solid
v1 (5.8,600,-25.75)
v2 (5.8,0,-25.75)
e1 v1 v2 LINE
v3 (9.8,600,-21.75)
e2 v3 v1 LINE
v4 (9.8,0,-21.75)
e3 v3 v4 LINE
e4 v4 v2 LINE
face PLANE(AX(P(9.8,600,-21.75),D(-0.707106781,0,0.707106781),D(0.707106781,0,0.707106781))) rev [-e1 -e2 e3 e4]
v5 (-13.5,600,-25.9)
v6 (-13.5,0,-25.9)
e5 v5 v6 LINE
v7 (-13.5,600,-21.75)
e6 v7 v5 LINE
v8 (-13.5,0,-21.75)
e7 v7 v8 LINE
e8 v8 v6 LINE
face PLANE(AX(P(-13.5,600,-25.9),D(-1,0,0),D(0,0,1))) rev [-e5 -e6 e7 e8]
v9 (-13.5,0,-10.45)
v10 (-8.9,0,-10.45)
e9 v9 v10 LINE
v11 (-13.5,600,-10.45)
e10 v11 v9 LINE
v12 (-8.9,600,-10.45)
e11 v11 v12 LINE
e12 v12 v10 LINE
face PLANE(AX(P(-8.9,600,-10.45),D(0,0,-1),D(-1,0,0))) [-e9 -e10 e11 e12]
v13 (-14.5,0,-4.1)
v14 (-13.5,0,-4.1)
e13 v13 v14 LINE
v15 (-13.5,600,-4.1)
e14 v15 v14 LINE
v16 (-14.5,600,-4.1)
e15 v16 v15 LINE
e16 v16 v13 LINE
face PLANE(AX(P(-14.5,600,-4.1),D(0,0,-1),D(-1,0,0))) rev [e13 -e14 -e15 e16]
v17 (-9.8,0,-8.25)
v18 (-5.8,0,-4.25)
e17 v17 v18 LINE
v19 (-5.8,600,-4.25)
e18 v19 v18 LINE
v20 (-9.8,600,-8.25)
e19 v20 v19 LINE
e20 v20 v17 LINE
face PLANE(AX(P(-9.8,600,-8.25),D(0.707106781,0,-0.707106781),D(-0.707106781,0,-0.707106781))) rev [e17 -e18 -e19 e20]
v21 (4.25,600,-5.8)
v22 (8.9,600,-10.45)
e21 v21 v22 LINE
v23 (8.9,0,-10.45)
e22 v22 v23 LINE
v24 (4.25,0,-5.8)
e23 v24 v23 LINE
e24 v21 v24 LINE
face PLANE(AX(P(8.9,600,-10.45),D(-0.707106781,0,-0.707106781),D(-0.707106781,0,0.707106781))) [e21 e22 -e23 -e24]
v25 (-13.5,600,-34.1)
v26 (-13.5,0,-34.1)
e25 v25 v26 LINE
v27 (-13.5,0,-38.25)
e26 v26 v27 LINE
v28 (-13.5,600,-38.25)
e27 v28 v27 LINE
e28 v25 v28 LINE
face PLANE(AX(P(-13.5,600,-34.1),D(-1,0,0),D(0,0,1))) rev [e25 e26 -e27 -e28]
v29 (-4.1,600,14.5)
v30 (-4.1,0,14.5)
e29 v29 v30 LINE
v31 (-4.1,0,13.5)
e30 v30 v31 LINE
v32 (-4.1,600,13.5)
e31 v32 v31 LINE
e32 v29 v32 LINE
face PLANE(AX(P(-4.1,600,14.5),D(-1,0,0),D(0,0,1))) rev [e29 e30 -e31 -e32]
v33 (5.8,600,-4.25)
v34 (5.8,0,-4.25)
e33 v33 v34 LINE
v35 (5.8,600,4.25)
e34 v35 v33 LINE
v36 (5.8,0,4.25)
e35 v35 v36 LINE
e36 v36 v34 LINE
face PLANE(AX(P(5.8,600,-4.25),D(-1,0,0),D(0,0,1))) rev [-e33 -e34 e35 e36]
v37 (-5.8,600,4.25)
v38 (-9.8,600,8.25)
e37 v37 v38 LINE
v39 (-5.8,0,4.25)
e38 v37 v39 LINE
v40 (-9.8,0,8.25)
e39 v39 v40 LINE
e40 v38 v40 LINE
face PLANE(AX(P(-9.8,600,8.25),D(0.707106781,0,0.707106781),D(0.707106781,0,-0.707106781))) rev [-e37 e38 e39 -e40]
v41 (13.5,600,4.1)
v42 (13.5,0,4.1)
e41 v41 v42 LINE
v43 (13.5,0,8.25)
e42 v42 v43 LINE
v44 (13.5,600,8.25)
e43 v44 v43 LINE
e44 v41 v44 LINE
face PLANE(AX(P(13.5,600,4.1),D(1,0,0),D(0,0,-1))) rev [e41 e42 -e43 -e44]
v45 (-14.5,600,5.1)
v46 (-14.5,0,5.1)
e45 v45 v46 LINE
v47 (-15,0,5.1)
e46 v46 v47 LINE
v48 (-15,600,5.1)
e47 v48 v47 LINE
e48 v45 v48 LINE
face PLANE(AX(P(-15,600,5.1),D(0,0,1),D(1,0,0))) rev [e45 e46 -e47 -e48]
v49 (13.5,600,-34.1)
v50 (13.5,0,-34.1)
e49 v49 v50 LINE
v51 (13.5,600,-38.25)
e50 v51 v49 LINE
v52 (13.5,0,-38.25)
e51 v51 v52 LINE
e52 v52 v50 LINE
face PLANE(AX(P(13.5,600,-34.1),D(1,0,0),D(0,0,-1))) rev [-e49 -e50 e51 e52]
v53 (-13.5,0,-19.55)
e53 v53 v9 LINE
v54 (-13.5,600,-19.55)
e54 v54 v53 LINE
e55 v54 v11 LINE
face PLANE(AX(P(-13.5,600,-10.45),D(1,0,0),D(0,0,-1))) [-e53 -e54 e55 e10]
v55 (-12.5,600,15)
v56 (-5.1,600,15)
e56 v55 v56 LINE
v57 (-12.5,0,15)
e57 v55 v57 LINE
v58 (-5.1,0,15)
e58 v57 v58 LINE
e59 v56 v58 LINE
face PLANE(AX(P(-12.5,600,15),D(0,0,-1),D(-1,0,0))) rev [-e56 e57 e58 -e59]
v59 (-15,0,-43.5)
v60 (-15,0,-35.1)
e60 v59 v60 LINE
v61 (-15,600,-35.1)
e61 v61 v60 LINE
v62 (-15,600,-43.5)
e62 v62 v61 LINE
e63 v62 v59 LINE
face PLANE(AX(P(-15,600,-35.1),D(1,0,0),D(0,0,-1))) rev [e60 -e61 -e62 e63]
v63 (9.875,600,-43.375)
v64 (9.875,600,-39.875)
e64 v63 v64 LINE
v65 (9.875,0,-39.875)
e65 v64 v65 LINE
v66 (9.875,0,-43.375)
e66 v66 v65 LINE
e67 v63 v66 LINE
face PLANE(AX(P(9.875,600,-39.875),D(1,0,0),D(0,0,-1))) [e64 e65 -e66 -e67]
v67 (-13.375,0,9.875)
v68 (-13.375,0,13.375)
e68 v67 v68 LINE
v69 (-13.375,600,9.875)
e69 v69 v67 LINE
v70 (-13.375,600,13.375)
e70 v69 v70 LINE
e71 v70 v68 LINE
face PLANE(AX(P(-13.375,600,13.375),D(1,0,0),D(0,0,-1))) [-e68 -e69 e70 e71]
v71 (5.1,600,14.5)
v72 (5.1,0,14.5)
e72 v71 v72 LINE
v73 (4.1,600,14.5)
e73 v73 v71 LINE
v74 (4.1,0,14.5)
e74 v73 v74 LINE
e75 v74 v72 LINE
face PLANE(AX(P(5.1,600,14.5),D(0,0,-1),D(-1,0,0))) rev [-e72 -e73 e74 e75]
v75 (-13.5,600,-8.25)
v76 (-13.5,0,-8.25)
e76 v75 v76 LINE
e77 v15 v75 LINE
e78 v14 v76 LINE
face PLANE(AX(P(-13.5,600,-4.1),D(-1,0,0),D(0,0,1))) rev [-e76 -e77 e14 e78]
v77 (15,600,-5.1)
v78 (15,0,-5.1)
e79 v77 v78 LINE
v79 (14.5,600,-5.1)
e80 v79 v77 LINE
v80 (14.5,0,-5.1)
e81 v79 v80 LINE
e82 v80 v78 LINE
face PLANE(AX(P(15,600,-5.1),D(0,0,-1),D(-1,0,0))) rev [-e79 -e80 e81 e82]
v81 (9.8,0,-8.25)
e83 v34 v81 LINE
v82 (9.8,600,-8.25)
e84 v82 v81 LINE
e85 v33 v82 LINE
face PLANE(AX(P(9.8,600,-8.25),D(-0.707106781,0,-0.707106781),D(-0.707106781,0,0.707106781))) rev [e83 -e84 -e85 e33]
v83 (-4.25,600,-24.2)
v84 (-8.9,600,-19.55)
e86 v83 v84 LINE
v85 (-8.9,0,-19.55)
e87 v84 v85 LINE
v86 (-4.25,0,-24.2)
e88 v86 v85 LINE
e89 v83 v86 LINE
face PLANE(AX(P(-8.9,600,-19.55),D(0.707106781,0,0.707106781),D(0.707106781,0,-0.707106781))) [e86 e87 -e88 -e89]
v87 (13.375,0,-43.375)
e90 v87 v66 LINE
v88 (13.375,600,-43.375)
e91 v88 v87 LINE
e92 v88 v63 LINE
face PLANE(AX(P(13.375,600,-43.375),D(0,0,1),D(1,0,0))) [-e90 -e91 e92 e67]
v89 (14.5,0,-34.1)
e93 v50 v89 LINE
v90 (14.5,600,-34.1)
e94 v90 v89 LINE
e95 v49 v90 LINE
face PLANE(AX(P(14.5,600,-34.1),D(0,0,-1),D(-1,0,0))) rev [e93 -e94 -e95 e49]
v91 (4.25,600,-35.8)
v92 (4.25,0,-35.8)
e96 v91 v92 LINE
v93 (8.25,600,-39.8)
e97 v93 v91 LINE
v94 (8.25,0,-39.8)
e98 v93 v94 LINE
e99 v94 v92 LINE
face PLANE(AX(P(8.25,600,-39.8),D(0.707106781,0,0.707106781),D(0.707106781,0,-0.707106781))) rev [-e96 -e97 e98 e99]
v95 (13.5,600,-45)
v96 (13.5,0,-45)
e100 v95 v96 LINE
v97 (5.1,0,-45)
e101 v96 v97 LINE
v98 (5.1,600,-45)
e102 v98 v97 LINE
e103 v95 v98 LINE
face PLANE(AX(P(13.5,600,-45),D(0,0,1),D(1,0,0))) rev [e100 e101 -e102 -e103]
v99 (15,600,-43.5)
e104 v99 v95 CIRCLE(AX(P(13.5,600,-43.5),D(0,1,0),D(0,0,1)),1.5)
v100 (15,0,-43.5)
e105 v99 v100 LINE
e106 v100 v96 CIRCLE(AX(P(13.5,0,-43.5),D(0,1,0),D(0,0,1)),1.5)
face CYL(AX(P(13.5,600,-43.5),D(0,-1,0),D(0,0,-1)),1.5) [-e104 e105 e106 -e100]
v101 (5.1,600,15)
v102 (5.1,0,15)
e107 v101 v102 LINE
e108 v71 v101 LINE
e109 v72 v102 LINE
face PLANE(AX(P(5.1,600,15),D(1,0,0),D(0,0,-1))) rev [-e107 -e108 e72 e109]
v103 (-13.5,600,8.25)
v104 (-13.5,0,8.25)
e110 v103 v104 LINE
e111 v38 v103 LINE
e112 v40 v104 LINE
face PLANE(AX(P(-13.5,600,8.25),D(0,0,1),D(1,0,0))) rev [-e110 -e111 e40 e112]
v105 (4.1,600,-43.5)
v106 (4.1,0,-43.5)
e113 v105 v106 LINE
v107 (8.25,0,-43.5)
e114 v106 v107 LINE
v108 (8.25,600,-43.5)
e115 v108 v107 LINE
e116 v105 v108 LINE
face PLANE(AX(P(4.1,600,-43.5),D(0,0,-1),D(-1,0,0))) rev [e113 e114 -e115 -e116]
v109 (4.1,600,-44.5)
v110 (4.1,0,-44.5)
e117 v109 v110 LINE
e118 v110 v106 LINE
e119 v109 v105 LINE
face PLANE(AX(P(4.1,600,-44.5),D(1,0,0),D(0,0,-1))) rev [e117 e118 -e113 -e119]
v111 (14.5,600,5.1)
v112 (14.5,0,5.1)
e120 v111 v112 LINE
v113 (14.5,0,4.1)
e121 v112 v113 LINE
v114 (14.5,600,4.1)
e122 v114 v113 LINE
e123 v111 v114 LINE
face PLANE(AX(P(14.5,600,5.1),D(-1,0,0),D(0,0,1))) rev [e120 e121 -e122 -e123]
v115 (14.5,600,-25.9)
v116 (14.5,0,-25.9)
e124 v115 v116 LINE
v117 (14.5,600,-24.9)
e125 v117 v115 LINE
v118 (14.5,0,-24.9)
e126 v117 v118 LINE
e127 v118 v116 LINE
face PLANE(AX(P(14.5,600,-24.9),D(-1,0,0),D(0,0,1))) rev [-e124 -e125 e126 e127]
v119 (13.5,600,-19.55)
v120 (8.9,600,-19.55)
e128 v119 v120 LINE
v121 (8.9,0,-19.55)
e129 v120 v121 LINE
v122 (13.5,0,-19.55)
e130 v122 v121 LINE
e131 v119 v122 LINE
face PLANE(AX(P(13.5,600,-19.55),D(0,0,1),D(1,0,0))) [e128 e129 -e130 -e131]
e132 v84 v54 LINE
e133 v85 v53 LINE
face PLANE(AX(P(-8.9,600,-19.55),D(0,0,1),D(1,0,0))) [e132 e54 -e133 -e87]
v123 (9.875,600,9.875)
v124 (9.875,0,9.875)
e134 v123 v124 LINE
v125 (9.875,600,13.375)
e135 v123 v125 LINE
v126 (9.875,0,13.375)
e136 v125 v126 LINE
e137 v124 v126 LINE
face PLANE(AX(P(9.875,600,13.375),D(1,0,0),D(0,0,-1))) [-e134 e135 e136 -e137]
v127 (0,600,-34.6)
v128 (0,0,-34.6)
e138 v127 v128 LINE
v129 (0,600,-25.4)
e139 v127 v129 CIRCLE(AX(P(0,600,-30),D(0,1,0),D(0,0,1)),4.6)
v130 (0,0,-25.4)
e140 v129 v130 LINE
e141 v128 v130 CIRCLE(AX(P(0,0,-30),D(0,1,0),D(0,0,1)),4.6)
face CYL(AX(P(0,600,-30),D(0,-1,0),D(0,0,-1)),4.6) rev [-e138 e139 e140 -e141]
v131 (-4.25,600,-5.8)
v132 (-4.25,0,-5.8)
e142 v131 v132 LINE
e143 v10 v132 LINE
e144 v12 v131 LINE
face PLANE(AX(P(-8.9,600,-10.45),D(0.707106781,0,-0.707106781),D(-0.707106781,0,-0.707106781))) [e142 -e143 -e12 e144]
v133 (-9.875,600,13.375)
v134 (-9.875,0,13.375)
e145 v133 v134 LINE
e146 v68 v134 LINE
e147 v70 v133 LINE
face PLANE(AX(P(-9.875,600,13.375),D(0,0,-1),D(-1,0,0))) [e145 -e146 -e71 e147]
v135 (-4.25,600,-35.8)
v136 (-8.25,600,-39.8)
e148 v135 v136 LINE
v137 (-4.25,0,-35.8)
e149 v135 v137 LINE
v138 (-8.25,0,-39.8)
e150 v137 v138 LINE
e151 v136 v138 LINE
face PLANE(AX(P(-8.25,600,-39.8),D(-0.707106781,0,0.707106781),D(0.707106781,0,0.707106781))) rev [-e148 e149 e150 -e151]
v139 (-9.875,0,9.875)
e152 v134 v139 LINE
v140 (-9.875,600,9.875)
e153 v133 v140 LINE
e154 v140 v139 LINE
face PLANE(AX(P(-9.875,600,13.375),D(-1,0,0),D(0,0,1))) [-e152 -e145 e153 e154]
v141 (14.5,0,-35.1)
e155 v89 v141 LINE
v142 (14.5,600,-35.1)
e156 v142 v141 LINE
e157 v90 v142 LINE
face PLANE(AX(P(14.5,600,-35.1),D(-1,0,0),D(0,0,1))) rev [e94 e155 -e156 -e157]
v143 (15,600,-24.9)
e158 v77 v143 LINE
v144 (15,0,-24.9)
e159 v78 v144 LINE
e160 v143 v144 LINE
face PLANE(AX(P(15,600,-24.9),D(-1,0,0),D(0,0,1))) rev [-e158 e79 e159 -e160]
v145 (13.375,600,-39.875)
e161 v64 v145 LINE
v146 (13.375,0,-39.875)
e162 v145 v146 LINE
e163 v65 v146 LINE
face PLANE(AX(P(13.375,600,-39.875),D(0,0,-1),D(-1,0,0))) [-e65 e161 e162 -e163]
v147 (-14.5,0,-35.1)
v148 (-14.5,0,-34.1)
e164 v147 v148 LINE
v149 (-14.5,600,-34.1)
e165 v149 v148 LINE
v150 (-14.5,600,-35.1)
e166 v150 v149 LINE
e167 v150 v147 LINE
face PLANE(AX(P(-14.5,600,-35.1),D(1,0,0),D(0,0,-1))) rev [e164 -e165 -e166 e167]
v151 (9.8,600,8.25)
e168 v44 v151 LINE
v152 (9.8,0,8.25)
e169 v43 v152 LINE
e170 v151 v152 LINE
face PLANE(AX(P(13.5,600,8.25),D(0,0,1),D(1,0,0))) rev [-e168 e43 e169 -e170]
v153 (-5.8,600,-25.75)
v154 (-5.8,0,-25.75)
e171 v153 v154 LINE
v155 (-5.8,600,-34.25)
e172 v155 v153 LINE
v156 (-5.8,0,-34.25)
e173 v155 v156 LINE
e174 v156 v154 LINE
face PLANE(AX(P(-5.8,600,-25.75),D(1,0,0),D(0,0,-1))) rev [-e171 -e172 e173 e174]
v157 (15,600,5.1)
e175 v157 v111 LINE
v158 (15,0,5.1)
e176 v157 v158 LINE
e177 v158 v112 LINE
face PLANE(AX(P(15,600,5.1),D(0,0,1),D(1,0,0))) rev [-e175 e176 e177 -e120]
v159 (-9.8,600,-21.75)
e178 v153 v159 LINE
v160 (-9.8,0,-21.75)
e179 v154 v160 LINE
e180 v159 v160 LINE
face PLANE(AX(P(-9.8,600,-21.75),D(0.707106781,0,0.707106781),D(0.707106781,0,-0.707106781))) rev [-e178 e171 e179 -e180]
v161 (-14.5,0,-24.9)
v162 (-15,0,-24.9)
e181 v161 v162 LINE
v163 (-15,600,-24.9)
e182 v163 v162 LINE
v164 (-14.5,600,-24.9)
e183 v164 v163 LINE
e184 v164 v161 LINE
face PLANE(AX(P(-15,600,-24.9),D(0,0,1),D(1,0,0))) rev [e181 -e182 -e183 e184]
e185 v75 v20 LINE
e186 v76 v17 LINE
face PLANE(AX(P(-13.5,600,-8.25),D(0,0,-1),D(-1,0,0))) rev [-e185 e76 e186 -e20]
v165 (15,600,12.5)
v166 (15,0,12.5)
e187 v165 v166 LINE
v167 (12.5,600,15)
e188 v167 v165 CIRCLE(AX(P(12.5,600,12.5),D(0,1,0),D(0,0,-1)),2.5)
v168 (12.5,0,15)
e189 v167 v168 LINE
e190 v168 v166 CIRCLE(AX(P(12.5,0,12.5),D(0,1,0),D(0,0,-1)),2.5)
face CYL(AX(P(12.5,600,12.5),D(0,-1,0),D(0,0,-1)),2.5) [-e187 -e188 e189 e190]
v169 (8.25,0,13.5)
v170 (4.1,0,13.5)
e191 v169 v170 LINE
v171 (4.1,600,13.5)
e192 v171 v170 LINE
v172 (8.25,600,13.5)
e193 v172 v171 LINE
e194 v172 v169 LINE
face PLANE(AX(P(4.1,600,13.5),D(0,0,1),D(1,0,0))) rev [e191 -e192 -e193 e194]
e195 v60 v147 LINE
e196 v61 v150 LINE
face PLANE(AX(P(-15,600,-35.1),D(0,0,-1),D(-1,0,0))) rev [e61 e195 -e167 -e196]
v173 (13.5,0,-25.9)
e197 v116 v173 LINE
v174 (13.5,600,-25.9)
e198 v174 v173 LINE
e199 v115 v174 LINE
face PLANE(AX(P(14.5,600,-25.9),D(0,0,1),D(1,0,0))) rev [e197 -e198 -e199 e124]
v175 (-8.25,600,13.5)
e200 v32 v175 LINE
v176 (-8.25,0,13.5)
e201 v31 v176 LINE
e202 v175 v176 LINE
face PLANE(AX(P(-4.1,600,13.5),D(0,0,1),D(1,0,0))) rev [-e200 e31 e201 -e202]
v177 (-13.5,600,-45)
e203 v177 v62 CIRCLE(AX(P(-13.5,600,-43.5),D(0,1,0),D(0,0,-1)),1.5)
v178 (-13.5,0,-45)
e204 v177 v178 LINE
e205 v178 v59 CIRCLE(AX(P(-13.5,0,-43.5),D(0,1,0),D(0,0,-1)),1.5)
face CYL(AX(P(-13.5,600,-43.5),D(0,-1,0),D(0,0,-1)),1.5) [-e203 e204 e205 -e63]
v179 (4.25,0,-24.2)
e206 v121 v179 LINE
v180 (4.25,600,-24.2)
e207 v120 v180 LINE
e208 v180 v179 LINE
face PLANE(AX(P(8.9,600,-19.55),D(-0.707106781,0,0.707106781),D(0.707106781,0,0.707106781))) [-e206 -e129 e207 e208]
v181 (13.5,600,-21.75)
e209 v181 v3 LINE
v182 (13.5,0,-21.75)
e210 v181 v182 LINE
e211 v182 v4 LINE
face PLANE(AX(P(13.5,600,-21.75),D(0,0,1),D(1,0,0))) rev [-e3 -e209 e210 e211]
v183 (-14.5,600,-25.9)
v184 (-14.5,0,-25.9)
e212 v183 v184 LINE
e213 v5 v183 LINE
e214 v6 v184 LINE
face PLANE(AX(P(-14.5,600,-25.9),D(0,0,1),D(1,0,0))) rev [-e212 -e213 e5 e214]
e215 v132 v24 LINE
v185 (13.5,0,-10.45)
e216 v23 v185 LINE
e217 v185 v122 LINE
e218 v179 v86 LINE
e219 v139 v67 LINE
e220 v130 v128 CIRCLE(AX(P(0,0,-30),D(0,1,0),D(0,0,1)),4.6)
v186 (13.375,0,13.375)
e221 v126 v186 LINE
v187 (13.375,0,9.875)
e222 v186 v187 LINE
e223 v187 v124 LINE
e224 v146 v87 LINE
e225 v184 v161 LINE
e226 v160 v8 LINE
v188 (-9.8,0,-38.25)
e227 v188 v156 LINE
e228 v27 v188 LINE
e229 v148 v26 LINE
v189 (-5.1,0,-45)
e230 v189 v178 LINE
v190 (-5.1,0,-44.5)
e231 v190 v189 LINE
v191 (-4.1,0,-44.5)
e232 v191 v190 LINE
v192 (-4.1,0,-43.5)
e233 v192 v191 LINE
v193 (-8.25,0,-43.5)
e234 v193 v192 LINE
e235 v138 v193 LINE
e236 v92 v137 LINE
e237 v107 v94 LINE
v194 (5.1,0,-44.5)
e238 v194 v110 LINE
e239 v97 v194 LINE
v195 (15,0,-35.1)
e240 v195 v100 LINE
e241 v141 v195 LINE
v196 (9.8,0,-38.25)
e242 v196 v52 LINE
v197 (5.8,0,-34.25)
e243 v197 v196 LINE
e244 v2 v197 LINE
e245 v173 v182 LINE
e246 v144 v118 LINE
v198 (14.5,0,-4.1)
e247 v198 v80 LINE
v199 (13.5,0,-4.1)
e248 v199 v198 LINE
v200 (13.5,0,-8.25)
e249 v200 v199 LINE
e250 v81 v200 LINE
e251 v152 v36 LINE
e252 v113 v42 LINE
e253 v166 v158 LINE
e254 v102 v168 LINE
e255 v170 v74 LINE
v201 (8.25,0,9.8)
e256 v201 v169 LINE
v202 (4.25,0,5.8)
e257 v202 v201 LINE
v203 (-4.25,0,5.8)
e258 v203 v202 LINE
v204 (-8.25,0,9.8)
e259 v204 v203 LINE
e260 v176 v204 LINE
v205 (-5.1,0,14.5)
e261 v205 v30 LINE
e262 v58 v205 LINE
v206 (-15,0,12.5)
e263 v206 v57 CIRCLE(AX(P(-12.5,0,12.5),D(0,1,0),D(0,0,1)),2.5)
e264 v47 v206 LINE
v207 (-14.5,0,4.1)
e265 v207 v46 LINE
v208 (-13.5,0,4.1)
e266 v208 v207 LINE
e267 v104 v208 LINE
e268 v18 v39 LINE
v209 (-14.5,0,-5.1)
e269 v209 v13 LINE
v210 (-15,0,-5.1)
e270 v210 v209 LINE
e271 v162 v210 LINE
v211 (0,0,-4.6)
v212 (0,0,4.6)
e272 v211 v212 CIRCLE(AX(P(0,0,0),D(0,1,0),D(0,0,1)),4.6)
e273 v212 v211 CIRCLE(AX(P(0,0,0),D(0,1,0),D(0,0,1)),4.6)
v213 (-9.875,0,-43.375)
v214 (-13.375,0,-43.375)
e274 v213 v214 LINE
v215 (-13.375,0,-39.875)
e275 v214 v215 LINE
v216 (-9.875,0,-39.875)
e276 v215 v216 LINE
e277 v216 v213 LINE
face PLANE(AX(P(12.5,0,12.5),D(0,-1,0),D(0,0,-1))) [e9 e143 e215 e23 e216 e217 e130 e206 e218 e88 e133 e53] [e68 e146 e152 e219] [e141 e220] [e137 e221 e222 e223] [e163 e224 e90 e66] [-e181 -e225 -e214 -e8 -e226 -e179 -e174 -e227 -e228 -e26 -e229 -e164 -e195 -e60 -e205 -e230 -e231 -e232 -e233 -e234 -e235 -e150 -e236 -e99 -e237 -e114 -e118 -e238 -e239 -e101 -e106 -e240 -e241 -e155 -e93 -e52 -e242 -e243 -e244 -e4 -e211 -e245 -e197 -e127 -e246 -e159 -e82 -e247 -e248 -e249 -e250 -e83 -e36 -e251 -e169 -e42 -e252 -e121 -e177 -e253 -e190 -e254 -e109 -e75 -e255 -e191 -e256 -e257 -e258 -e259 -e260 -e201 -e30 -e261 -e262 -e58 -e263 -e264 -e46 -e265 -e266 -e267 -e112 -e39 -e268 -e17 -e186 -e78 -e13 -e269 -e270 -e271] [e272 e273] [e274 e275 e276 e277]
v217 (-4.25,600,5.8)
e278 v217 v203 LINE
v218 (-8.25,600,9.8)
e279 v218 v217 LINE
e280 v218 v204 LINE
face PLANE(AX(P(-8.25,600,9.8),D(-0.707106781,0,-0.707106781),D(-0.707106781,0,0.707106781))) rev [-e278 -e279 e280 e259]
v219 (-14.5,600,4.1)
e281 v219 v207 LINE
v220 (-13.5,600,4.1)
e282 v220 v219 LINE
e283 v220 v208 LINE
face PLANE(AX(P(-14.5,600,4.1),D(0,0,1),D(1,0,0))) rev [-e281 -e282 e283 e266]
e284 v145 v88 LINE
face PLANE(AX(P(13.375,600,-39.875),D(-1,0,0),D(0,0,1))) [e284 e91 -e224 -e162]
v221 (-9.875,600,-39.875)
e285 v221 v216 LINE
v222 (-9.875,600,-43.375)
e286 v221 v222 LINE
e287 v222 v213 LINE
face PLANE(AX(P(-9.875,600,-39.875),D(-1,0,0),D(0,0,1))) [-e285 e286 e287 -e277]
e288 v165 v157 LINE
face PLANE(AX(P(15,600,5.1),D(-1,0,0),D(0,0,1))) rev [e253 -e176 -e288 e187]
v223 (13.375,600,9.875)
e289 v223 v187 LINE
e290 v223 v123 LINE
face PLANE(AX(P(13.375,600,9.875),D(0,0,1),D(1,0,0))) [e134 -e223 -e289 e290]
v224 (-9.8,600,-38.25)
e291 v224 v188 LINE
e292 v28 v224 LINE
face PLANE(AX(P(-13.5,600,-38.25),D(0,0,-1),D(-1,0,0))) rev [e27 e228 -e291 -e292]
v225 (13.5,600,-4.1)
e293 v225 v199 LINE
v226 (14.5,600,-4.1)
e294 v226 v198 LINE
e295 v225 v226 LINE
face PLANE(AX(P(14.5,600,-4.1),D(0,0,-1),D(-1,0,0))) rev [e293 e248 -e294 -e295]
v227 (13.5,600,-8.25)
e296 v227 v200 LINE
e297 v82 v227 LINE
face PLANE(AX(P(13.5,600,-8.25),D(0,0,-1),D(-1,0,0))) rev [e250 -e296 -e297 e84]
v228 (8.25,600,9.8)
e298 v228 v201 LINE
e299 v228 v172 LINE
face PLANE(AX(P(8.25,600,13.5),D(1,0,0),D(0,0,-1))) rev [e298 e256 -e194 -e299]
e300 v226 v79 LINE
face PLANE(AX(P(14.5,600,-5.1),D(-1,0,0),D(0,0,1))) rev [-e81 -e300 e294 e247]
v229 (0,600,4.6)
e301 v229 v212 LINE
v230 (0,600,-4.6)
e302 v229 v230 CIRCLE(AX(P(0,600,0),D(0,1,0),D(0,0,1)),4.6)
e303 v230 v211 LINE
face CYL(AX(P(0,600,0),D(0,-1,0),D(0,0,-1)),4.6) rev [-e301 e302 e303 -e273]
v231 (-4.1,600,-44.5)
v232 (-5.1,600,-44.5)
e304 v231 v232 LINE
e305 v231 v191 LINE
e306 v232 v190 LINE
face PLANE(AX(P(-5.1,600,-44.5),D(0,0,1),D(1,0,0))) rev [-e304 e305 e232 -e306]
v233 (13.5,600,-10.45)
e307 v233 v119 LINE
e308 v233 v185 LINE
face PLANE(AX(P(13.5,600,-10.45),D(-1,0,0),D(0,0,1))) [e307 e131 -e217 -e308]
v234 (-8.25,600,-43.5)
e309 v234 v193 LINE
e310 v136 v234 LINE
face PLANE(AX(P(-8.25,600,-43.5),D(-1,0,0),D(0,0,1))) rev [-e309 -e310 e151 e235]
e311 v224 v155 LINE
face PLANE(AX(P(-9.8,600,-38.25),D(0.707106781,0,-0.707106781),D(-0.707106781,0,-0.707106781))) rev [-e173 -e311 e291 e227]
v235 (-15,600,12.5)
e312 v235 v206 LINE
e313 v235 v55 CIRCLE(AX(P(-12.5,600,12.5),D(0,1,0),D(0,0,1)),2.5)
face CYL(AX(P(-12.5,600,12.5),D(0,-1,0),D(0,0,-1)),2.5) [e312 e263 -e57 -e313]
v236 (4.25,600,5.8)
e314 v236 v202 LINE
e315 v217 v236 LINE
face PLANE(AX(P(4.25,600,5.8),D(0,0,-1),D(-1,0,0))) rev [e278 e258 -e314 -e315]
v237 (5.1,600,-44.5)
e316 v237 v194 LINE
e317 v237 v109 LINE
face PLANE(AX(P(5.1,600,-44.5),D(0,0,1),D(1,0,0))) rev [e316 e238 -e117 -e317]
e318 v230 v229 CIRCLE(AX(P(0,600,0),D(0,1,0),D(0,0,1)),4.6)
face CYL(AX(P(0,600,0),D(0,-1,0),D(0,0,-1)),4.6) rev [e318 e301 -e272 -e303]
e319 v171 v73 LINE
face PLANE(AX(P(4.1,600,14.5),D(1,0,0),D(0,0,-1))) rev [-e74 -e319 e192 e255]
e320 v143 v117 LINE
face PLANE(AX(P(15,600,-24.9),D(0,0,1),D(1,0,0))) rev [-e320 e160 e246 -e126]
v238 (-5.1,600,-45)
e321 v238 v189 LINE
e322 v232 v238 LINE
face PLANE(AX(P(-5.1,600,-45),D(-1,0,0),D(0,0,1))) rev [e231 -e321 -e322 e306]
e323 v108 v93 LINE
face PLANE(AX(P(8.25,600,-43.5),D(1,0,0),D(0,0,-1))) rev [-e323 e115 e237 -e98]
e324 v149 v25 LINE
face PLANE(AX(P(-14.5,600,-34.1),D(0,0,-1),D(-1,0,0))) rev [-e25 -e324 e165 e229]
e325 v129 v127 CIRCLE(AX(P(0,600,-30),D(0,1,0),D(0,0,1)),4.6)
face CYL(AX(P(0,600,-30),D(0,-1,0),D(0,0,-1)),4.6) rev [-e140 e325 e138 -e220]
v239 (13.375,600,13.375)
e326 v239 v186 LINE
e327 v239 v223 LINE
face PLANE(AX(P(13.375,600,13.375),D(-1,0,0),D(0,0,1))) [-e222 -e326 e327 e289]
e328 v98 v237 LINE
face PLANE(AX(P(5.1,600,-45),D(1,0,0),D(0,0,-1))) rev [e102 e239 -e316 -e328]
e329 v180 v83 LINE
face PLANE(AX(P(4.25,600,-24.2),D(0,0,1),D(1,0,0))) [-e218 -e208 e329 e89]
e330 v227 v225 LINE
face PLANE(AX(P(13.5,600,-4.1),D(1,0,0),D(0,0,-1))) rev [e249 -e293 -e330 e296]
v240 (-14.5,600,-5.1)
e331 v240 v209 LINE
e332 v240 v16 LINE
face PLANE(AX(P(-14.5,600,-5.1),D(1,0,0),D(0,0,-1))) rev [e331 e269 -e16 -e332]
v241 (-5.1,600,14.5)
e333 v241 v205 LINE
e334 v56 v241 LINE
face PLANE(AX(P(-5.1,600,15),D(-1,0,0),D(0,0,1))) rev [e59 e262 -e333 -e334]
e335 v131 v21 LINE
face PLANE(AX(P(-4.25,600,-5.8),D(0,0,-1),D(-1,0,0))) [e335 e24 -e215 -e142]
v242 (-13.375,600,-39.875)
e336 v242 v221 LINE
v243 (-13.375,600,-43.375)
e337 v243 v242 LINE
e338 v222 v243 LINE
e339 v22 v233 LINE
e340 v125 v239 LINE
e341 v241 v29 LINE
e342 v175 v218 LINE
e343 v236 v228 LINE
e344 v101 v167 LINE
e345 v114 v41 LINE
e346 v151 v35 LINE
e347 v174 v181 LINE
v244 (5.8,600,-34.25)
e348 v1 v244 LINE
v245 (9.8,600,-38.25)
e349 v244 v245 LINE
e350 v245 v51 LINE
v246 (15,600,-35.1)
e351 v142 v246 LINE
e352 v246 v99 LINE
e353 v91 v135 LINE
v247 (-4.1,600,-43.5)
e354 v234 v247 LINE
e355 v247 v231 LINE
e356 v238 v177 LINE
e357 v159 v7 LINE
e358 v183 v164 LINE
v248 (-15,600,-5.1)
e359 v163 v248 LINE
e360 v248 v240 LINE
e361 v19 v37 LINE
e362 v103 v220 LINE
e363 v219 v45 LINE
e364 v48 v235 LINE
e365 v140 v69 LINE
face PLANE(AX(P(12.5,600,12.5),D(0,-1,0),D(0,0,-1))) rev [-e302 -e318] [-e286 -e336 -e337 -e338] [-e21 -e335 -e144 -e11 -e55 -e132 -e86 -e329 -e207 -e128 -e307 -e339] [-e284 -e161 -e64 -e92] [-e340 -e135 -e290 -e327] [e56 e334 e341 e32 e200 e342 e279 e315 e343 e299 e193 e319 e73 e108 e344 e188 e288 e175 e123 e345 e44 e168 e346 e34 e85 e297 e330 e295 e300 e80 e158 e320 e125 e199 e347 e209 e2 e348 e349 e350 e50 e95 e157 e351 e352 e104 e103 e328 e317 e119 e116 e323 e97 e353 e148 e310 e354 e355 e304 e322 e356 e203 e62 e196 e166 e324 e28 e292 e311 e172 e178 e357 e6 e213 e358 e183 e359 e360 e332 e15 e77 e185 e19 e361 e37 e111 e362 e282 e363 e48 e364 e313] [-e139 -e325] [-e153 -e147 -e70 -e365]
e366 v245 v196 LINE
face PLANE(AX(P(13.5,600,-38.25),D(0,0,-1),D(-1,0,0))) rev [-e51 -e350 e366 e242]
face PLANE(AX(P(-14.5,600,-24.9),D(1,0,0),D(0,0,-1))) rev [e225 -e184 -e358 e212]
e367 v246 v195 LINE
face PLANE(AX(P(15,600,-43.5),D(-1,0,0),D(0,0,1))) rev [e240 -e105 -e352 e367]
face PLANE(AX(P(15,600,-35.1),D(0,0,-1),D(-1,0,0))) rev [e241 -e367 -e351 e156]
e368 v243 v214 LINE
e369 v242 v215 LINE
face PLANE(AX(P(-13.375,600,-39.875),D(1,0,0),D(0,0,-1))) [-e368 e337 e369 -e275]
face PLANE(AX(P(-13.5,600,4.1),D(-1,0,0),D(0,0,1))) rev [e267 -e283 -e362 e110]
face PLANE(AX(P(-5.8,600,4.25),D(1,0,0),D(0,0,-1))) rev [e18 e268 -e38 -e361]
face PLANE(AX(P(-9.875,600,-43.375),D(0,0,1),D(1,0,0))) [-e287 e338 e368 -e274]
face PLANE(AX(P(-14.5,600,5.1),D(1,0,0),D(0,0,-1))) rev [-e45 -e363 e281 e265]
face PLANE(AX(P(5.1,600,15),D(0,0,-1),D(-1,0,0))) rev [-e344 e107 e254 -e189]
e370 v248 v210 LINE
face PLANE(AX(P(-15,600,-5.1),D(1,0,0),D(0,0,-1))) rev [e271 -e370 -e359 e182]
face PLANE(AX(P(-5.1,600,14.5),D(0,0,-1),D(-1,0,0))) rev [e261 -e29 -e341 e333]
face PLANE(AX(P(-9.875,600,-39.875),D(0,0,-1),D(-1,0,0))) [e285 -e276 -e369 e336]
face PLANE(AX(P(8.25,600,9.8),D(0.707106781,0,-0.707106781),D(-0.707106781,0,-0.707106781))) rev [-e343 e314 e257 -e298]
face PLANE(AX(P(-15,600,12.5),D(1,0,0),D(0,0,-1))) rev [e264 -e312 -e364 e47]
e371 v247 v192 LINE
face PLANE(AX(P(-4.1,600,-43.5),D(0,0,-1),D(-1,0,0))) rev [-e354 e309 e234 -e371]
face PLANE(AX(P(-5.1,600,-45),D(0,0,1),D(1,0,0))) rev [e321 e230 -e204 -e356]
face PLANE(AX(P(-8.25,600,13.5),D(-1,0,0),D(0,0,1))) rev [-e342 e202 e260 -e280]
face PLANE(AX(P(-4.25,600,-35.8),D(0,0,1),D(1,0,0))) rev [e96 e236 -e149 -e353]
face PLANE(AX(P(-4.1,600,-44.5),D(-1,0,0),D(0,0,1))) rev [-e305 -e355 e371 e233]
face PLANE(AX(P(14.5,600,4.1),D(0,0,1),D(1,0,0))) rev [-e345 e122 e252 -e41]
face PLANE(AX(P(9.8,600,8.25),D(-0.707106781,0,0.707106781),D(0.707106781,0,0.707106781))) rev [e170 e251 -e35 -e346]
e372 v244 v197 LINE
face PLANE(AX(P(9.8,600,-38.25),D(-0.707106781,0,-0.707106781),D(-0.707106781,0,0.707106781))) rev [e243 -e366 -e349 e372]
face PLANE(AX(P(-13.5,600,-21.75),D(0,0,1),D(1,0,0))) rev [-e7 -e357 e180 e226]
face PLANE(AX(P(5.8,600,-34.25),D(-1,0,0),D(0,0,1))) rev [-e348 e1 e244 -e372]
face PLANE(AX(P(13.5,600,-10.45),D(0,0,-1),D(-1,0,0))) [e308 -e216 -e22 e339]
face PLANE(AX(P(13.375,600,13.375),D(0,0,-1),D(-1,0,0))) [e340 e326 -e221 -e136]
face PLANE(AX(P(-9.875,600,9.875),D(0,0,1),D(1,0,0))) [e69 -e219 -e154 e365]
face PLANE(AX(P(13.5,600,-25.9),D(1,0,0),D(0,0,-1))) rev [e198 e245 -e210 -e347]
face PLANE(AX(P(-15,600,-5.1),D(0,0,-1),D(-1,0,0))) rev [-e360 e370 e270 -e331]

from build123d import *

# Parameters (mm, degrees)
SKETCH1_R                                = 4.6
SKETCH1_W                                = 3.5
SKETCH1_H                                = 3.5
ALUMINUM_PROFILE_30_X_60L_X_R2_5_1_DEPTH = 600


with BuildPart() as part:
    # Sketch1 → Aluminum profile 30 X 60L X R2.5(1) (new body)
    with BuildSketch(Plane(origin=(0, 0, 0), x_dir=(-1, 0, 0), z_dir=(0, 1, 0))):
        with BuildLine():
            Line((-5.1, 15), (-5.1, 14.5))
            Line((-5.1, 14.5), (-4.1, 14.5))
            Line((-4.1, 14.5), (-4.1, 13.5))
            Line((-4.1, 13.5), (-8.25, 13.5))
            Line((-8.25, 13.5), (-8.25, 9.8))
            Line((-8.25, 9.8), (-4.25, 5.8))
            Line((-4.25, 5.8), (4.25, 5.8))
            Line((4.25, 5.8), (8.25, 9.8))
            Line((8.25, 9.8), (8.25, 13.5))
            Line((8.25, 13.5), (4.1, 13.5))
            Line((4.1, 13.5), (4.1, 14.5))
            Line((4.1, 14.5), (5.1, 14.5))
            Line((5.1, 14.5), (5.1, 15))
            Line((5.1, 15), (12.5, 15))
            ThreePointArc((12.5, 15), (14.267766953, 14.267766953), (15, 12.5))
            Line((15, 12.5), (15, 5.1))
            Line((15, 5.1), (14.5, 5.1))
            Line((14.5, 5.1), (14.5, 4.1))
            Line((14.5, 4.1), (13.5, 4.1))
            Line((13.5, 4.1), (13.5, 8.25))
            Line((13.5, 8.25), (9.8, 8.25))
            Line((9.8, 8.25), (5.8, 4.25))
            Line((5.8, 4.25), (5.8, -4.25))
            Line((5.8, -4.25), (9.8, -8.25))
            Line((9.8, -8.25), (13.5, -8.25))
            Line((13.5, -8.25), (13.5, -4.1))
            Line((13.5, -4.1), (14.5, -4.1))
            Line((14.5, -4.1), (14.5, -5.1))
            Line((14.5, -5.1), (15, -5.1))
            Line((15, -5.1), (15, -24.9))
            Line((15, -24.9), (14.5, -24.9))
            Line((14.5, -24.9), (14.5, -25.9))
            Line((14.5, -25.9), (13.5, -25.9))
            Line((13.5, -25.9), (13.5, -21.75))
            Line((13.5, -21.75), (9.8, -21.75))
            Line((9.8, -21.75), (5.8, -25.75))
            Line((5.8, -25.75), (5.8, -34.25))
            Line((5.8, -34.25), (9.8, -38.25))
            Line((9.8, -38.25), (13.5, -38.25))
            Line((13.5, -38.25), (13.5, -34.1))
            Line((13.5, -34.1), (14.5, -34.1))
            Line((14.5, -34.1), (14.5, -35.1))
            Line((14.5, -35.1), (15, -35.1))
            Line((15, -35.1), (15, -43.5))
            ThreePointArc((15, -43.5), (14.560660172, -44.560660172), (13.5, -45))
            Line((13.5, -45), (5.1, -45))
            Line((5.1, -45), (5.1, -44.5))
            Line((5.1, -44.5), (4.1, -44.5))
            Line((4.1, -44.5), (4.1, -43.5))
            Line((4.1, -43.5), (8.25, -43.5))
            Line((8.25, -43.5), (8.25, -39.8))
            Line((8.25, -39.8), (4.25, -35.8))
            Line((4.25, -35.8), (-4.25, -35.8))
            Line((-4.25, -35.8), (-8.25, -39.8))
            Line((-8.25, -39.8), (-8.25, -43.5))
            Line((-8.25, -43.5), (-4.1, -43.5))
            Line((-4.1, -43.5), (-4.1, -44.5))
            Line((-4.1, -44.5), (-5.1, -44.5))
            Line((-5.1, -44.5), (-5.1, -45))
            Line((-5.1, -45), (-13.5, -45))
            ThreePointArc((-13.5, -45), (-14.560660172, -44.560660172), (-15, -43.5))
            Line((-15, -43.5), (-15, -35.1))
            Line((-15, -35.1), (-14.5, -35.1))
            Line((-14.5, -35.1), (-14.5, -34.1))
            Line((-14.5, -34.1), (-13.5, -34.1))
            Line((-13.5, -34.1), (-13.5, -38.25))
            Line((-13.5, -38.25), (-9.8, -38.25))
            Line((-9.8, -38.25), (-5.8, -34.25))
            Line((-5.8, -34.25), (-5.8, -25.75))
            Line((-5.8, -25.75), (-9.8, -21.75))
            Line((-9.8, -21.75), (-13.5, -21.75))
            Line((-13.5, -21.75), (-13.5, -25.9))
            Line((-13.5, -25.9), (-14.5, -25.9))
            Line((-14.5, -25.9), (-14.5, -24.9))
            Line((-14.5, -24.9), (-15, -24.9))
            Line((-15, -24.9), (-15, -5.1))
            Line((-15, -5.1), (-14.5, -5.1))
            Line((-14.5, -5.1), (-14.5, -4.1))
            Line((-14.5, -4.1), (-13.5, -4.1))
            Line((-13.5, -4.1), (-13.5, -8.25))
            Line((-13.5, -8.25), (-9.8, -8.25))
            Line((-9.8, -8.25), (-5.8, -4.25))
            Line((-5.8, -4.25), (-5.8, 4.25))
            Line((-5.8, 4.25), (-9.8, 8.25))
            Line((-9.8, 8.25), (-13.5, 8.25))
            Line((-13.5, 8.25), (-13.5, 4.1))
            Line((-13.5, 4.1), (-14.5, 4.1))
            Line((-14.5, 4.1), (-14.5, 5.1))
            Line((-14.5, 5.1), (-15, 5.1))
            Line((-15, 5.1), (-15, 12.5))
            ThreePointArc((-15, 12.5), (-14.267766953, 14.267766953), (-12.5, 15))
            Line((-12.5, 15), (-5.1, 15))
        make_face()
        Circle(SKETCH1_R, mode=Mode.SUBTRACT)
        with Locations((0, -30)):
            Circle(SKETCH1_R, mode=Mode.SUBTRACT)
        Polygon((8.9, -10.45), (4.25, -5.8), (-4.25, -5.8), (-8.9, -10.45), (-13.5, -10.45), (-13.5, -19.55), (-8.9, -19.55), (-4.25, -24.2), (4.25, -24.2), (8.9, -19.55), (13.5, -19.55), (13.5, -10.45), align=None, mode=Mode.SUBTRACT)
        with Locations((-11.625, 11.625)):
            Rectangle(SKETCH1_W, SKETCH1_H, mode=Mode.SUBTRACT)
        with Locations((11.625, 11.625)):
            Rectangle(SKETCH1_W, SKETCH1_H, mode=Mode.SUBTRACT)
        with Locations((-11.625, -41.625)):
            Rectangle(SKETCH1_W, SKETCH1_H, mode=Mode.SUBTRACT)
        with Locations((11.625, -41.625)):
            Rectangle(SKETCH1_W, SKETCH1_H, mode=Mode.SUBTRACT)
    extrude(amount=ALUMINUM_PROFILE_30_X_60L_X_R2_5_1_DEPTH)


solid = part.part
